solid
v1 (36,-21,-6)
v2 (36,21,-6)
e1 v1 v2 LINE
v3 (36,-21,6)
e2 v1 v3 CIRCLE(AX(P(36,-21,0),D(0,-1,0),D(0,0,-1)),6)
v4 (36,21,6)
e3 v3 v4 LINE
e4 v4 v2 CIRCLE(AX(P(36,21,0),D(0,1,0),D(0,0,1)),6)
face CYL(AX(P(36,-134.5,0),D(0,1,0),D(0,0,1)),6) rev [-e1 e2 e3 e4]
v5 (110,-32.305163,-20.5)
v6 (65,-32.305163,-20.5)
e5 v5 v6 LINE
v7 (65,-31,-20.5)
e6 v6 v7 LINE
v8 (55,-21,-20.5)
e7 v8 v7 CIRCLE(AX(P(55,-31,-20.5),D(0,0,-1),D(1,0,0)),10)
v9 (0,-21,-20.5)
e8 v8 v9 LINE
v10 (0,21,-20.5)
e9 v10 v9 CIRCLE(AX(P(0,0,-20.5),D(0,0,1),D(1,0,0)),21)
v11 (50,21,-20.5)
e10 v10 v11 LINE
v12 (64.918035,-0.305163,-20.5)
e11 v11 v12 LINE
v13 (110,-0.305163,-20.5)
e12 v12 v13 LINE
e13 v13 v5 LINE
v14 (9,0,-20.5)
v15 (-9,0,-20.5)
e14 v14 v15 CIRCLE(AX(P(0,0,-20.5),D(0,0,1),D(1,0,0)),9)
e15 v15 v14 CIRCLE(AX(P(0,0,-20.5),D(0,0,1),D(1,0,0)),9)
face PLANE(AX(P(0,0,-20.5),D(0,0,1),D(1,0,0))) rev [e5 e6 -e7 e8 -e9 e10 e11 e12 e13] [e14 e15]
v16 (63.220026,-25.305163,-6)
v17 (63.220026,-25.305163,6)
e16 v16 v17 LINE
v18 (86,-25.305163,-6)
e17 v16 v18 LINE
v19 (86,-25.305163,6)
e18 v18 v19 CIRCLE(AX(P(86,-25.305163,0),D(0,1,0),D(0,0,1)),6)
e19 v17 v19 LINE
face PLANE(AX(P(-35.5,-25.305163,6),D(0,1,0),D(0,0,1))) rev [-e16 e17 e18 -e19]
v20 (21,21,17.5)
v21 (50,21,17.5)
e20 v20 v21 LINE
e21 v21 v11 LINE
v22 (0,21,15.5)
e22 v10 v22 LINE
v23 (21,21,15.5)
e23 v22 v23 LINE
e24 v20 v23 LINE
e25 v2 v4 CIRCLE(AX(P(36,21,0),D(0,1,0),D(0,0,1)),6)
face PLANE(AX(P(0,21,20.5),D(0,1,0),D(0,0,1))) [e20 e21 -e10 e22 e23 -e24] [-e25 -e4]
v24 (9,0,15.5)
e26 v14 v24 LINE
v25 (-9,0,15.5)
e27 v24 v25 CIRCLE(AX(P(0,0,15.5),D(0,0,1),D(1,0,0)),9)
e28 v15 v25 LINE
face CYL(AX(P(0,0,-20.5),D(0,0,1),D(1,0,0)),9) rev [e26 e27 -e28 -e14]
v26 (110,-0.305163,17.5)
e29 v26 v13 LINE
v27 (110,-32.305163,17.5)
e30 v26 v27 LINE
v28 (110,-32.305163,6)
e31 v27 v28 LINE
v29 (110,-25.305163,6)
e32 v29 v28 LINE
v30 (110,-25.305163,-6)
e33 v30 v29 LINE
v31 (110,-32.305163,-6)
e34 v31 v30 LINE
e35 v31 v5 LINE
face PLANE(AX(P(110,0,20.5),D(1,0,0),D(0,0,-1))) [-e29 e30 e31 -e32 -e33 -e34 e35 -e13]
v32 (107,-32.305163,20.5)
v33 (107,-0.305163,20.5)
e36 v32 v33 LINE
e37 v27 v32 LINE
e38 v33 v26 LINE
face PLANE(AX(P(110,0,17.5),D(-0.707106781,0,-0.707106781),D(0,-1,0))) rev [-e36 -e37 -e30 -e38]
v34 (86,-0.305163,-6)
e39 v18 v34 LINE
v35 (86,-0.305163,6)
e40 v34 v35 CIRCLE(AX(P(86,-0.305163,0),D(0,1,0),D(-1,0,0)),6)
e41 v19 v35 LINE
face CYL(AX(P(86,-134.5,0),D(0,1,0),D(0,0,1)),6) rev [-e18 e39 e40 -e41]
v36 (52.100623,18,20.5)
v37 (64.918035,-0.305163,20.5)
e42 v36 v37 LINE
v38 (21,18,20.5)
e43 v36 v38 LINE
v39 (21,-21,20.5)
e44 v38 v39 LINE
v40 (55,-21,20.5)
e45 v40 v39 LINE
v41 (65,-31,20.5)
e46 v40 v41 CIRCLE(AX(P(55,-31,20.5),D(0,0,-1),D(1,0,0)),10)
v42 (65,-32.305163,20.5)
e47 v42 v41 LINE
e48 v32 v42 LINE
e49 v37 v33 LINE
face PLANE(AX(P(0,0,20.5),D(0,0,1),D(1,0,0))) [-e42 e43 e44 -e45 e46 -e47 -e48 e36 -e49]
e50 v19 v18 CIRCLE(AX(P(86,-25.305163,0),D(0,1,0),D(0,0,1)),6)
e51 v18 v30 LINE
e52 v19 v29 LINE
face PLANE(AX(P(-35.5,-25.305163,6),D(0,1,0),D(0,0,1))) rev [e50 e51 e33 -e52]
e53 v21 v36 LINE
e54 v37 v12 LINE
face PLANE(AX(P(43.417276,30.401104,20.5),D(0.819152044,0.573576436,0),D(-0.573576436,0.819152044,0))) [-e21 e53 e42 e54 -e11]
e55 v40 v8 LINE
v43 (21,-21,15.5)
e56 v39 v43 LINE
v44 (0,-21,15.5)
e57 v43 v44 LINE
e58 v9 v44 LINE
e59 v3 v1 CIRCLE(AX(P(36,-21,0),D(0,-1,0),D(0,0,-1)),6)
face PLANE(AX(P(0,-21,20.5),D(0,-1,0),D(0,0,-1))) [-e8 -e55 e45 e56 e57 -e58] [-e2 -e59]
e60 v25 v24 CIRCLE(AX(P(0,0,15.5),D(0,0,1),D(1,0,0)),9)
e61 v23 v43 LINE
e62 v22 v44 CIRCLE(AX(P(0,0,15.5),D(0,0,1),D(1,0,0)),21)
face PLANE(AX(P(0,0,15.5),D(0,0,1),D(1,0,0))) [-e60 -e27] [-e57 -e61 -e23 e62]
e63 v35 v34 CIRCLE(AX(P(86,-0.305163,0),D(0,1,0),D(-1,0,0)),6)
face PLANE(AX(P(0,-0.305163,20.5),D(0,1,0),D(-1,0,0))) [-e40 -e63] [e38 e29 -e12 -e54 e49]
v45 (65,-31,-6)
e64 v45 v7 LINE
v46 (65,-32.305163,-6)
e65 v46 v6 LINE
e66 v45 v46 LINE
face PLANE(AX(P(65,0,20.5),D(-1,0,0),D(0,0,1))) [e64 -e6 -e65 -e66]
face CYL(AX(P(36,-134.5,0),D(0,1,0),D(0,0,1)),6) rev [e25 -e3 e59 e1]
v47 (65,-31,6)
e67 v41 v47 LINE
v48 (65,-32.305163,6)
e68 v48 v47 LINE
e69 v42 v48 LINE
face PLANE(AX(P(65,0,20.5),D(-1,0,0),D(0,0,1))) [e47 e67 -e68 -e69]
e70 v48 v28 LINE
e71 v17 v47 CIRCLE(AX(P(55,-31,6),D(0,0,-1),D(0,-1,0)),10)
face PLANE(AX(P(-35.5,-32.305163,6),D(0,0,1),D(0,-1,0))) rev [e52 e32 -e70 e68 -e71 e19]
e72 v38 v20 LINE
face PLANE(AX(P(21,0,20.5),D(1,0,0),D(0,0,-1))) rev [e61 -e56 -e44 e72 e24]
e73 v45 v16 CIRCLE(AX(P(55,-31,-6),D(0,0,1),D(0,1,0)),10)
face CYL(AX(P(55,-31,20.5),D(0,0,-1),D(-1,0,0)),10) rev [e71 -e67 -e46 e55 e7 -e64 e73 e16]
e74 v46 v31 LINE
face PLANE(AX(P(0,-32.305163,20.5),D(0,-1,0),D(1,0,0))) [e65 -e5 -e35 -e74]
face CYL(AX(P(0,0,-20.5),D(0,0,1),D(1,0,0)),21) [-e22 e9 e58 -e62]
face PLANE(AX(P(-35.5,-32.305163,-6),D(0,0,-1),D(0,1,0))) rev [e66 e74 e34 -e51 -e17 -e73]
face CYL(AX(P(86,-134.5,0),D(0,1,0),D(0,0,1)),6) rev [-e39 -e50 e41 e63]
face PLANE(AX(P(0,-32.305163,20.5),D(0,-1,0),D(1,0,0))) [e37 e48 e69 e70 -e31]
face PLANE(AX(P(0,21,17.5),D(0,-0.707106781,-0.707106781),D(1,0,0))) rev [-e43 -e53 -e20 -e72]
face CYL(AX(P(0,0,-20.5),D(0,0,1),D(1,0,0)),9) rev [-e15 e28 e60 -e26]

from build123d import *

# Parameters (mm, degrees)
LEVER_BODY_41MM_DEPTH     = 20.5
PIVOT_EYE_BOSS_DEPTH      = 15.5
PIVOT_EYE_BOSS_DEPTH_BACK = 20.5
SKETCH1_4_R               = 9
EDGE_CHAMFER_3X45_A_SIZE  = 3
EDGE_CHAMFER_3X45_B_SIZE  = 3
UNDERSIDE_SLOT_SKETCH_W   = 12
UNDERSIDE_SLOT_SKETCH_H   = 7
UNDERSIDE_SLOT_DEPTH      = 145.5
TOP_HOLES_SKETCH_R        = 6
TOP_HOLES_2X_DEPTH        = 155.5


with BuildPart() as part:
    # Lever Profile Sketch → Lever Body 41mm (new, symmetric)
    with BuildSketch(Plane.XY):
        with BuildLine():
            Line((50, 21), (21, 21))
            Line((21, 21), (21, -21))
            Line((21, -21), (55, -21))
            ThreePointArc((55, -21), (62.071067812, -23.928932188), (65, -31))
            Line((65, -31), (65, -32.305162606))
            Line((65, -32.305162606), (110, -32.305162606))
            Line((110, -32.305162606), (110, -0.305162606))
            Line((110, -0.305162606), (64.918035459, -0.305162606))
            Line((64.918035459, -0.305162606), (50, 21))
        make_face()
    extrude(amount=LEVER_BODY_41MM_DEPTH, both=True)

    # Sketch1_4 → Pivot Eye Boss (add, two sides: drawn at the far end of the back side and taken through both)
    with BuildSketch(Plane.XY.offset(-PIVOT_EYE_BOSS_DEPTH_BACK)):
        with BuildLine():
            Line((21, 21), (0, 21))
            ThreePointArc((0, 21), (-21, 0), (0, -21))
            Line((0, -21), (21, -21))
            Line((21, -21), (21, 21))
        make_face()
        Circle(SKETCH1_4_R, mode=Mode.SUBTRACT)
    extrude(amount=PIVOT_EYE_BOSS_DEPTH + PIVOT_EYE_BOSS_DEPTH_BACK)

    # Edge Chamfer 3x45 A
    edge_chamfer_3x45_a_edges = [part.edges().sort_by_distance(p)[0] for p in [
        (35.5, 21, 20.5),
    ]]
    chamfer(edge_chamfer_3x45_a_edges, length=EDGE_CHAMFER_3X45_A_SIZE)

    # Edge Chamfer 3x45 B
    edge_chamfer_3x45_b_edges = [part.edges().sort_by_distance(p)[0] for p in [
        (110, -16.305162606, 20.5),
    ]]
    chamfer(edge_chamfer_3x45_b_edges, length=EDGE_CHAMFER_3X45_B_SIZE)

    # Underside Slot Sketch → Underside Slot (cut)
    with BuildSketch(Plane(origin=(110, 0, 0), x_dir=(0, 0, -1), z_dir=(1, 0, 0))):
        with Locations((0, -28.805162606)):
            Rectangle(UNDERSIDE_SLOT_SKETCH_W, UNDERSIDE_SLOT_SKETCH_H)
    extrude(amount=-UNDERSIDE_SLOT_DEPTH, mode=Mode.SUBTRACT)

    # Top Holes Sketch → Top Holes 2x (cut)
    with BuildSketch(Plane(origin=(0, 21, 0), x_dir=(1, 0, 0), z_dir=(0, 1, 0))):
        with Locations(Location((36, 0, 0), (0, 0, 270))):
            Circle(TOP_HOLES_SKETCH_R)
        with Locations(Location((86, 0, 0), (0, 0, 270))):
            Circle(TOP_HOLES_SKETCH_R)
    extrude(amount=-TOP_HOLES_2X_DEPTH, mode=Mode.SUBTRACT)


solid = part.part
